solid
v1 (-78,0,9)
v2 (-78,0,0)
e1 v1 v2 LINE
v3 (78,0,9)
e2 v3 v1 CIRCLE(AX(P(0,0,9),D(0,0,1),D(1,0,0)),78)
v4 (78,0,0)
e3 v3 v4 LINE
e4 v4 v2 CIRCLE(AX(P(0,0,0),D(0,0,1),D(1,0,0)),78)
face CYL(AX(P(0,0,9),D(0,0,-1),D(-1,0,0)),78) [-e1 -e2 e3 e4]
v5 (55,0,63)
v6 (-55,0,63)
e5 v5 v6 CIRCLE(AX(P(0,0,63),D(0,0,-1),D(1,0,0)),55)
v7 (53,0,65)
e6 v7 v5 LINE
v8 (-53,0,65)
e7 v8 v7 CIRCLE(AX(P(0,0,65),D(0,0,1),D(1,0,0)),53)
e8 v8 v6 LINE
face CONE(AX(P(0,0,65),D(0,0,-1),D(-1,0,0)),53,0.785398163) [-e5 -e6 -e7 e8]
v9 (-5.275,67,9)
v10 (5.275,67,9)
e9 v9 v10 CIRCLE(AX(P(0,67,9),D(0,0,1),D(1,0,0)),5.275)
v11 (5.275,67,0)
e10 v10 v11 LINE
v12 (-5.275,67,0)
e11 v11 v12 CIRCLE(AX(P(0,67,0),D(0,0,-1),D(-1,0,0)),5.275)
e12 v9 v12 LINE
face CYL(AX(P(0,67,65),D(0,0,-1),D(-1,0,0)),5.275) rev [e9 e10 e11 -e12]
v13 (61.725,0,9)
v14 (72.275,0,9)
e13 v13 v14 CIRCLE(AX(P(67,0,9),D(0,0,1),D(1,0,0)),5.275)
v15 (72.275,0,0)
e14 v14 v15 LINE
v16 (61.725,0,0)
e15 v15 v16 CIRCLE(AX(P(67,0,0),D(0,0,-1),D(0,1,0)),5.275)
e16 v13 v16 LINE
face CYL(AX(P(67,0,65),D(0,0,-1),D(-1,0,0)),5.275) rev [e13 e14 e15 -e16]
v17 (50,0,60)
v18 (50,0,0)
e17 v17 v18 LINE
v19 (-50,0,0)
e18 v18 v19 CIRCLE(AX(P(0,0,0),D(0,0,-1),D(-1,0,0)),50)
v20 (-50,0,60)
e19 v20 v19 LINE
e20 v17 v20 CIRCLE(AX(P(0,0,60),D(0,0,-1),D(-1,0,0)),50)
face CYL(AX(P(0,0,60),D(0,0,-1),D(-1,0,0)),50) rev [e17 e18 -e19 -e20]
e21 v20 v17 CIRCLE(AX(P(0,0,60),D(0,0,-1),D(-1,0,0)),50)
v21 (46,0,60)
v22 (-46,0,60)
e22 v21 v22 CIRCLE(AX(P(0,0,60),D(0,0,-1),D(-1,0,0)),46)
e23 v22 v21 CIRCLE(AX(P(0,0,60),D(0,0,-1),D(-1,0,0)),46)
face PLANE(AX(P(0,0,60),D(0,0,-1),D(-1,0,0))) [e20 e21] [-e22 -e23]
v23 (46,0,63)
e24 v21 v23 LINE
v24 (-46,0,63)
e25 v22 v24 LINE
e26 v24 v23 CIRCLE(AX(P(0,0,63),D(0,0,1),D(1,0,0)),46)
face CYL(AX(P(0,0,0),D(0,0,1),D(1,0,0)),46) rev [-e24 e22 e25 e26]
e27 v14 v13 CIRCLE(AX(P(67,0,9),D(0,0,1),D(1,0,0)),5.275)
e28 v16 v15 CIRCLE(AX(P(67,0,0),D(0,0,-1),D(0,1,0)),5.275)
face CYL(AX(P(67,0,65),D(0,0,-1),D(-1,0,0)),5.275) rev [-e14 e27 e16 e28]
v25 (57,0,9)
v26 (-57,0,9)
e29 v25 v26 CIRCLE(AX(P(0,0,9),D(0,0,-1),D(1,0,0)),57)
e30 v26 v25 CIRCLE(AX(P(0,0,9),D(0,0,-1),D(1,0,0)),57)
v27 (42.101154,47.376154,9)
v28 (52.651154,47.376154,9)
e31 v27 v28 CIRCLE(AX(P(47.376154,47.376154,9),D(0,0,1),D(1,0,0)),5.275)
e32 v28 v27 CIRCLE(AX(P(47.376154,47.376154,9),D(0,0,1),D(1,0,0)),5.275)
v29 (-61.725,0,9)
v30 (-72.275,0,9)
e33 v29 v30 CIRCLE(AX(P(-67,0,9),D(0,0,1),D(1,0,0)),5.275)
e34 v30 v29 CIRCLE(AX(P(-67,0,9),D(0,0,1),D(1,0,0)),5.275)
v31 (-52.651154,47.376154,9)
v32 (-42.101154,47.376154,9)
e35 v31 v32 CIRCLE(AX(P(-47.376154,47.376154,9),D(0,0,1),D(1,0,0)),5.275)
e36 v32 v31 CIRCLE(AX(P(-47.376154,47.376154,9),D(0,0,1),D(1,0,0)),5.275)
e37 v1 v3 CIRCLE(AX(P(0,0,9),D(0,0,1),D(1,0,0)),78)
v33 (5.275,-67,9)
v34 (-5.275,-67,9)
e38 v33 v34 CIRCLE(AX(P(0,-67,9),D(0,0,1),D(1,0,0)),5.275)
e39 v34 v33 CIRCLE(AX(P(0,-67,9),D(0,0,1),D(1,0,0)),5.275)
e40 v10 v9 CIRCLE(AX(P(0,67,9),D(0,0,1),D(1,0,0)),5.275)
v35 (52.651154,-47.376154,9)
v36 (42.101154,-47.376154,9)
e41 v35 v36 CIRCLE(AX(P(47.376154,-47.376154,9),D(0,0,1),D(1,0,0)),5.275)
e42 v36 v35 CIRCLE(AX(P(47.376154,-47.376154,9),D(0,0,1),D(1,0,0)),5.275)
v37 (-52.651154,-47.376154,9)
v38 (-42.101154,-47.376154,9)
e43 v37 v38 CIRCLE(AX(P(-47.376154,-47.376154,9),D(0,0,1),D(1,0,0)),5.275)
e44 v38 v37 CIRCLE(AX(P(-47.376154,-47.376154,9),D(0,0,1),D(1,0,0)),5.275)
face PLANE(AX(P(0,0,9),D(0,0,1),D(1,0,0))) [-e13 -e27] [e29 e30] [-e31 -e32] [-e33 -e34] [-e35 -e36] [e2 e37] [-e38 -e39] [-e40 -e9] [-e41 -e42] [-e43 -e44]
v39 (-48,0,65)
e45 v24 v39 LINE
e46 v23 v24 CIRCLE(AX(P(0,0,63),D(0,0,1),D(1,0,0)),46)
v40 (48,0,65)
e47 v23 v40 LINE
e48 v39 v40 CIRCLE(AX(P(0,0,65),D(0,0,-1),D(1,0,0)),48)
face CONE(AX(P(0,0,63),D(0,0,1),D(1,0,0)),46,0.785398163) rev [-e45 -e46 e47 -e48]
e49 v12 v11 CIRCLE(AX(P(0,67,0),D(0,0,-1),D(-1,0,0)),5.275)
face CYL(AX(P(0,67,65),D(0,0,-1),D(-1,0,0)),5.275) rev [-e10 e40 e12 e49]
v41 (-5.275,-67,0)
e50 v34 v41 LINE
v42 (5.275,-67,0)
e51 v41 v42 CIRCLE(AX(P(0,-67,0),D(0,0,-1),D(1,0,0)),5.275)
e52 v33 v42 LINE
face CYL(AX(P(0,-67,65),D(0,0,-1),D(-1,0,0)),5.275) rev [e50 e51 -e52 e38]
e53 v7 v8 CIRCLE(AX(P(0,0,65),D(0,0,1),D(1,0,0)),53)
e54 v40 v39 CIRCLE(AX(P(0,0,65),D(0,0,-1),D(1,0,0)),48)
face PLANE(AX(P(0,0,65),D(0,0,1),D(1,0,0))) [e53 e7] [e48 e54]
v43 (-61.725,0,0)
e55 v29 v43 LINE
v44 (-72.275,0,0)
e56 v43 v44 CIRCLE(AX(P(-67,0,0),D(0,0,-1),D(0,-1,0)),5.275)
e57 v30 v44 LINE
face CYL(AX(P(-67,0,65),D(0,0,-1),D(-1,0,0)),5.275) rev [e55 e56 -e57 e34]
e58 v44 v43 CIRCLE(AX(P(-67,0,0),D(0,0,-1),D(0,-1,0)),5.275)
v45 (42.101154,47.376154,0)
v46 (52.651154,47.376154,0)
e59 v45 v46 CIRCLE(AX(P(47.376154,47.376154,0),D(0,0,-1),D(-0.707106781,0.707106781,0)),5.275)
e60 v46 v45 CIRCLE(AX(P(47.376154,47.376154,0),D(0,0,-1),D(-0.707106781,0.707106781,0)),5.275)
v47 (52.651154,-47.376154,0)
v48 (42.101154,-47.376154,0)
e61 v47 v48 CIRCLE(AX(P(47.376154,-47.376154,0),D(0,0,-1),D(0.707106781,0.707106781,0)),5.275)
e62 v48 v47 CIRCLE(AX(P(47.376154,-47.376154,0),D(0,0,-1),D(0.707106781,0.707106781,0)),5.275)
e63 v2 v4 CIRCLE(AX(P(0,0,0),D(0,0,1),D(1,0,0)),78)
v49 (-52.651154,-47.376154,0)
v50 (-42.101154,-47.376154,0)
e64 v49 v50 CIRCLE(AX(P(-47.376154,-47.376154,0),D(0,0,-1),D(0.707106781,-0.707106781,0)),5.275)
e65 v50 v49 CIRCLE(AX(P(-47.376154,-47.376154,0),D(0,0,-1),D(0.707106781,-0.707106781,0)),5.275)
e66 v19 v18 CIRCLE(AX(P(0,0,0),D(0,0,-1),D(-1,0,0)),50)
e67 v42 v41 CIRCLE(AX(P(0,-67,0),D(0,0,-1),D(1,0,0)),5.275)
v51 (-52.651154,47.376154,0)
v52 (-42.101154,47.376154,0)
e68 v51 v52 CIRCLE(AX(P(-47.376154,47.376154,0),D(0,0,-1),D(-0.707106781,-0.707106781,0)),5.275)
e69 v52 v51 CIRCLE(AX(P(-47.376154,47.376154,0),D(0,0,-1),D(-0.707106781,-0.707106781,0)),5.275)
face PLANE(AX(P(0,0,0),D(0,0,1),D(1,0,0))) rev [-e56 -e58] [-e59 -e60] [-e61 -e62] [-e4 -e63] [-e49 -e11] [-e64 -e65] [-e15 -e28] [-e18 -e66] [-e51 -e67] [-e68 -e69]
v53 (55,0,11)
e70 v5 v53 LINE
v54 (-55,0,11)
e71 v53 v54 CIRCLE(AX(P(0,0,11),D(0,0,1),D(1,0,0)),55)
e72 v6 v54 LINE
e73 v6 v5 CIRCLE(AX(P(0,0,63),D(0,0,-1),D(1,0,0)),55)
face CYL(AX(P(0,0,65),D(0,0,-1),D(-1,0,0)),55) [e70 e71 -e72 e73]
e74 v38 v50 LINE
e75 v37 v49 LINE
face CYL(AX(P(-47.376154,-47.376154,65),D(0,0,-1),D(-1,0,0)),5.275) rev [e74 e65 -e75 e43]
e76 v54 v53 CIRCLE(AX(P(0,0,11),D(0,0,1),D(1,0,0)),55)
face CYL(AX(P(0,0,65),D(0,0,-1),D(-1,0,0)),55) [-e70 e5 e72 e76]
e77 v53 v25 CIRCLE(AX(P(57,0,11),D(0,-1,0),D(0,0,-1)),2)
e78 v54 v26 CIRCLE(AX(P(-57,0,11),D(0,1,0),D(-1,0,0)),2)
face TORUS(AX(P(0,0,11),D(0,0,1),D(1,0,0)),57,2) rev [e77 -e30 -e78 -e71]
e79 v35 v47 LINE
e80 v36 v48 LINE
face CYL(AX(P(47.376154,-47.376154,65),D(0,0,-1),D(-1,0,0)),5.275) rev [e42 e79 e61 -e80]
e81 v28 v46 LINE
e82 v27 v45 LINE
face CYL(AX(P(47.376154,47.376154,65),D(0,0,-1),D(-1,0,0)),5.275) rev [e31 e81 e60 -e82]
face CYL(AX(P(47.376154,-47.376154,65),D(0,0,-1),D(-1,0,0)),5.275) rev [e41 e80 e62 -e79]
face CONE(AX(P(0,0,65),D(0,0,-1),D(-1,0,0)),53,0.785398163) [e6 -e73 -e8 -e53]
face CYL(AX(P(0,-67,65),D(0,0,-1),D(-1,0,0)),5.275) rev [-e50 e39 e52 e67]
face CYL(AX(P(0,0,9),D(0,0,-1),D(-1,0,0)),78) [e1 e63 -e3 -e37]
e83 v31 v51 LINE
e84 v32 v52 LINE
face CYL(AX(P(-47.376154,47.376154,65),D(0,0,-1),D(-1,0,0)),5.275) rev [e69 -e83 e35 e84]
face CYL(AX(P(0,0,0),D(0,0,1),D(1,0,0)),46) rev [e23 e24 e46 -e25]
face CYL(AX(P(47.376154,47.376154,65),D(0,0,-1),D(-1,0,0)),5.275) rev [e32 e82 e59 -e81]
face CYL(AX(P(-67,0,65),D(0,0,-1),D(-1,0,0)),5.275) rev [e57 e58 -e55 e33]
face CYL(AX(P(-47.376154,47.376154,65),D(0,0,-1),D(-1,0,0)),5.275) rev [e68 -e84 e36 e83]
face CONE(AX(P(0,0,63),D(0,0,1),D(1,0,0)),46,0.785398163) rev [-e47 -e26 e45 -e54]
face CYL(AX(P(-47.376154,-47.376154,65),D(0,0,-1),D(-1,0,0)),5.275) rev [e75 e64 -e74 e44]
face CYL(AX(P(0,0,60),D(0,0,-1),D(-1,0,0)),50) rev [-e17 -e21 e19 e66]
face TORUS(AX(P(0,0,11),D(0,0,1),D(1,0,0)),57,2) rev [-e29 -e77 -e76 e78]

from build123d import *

# Parameters (mm, degrees)
SKETCH1_R           = 78
BOSS_EXTRUDE1_DEPTH = 9
SKETCH2_R           = 55
BOSS_EXTRUDE2_DEPTH = 56
SKETCH3_R           = 50
CUT_EXTRUDE2_DEPTH  = 60
SKETCH4_R           = 46
CUT_EXTRUDE3_DEPTH  = 129.035151423
SKETCH5_R           = 5.275
CUT_EXTRUDE4_DEPTH  = 129.035151423
CIRPATTERN1_COUNT   = 8
CHAMFER1_SIZE       = 2
FILLET1_R           = 2


with BuildPart() as part:
    # Sketch1 → Boss-Extrude1 (new body)
    with BuildSketch(Plane.XY):
        Circle(SKETCH1_R)
    extrude(amount=BOSS_EXTRUDE1_DEPTH)

    # Sketch2 → Boss-Extrude2 (add)
    with BuildSketch(Plane.XY.offset(9)):
        Circle(SKETCH2_R)
    extrude(amount=BOSS_EXTRUDE2_DEPTH)

    # Sketch3 → Cut-Extrude2 (cut)
    with BuildSketch(Plane(origin=(0, 0, 0), x_dir=(-1, 0, 0), z_dir=(0, 0, -1))):
        Circle(SKETCH3_R)
    extrude(amount=-CUT_EXTRUDE2_DEPTH, mode=Mode.SUBTRACT)

    # Sketch4 → Cut-Extrude3 (cut, through all)
    with BuildSketch(Plane.XY.offset(65)):
        Circle(SKETCH4_R)
    extrude(amount=-CUT_EXTRUDE3_DEPTH, mode=Mode.SUBTRACT)

    # Sketch5 → Cut-Extrude4 (cut, through all)
    with BuildSketch(Plane(origin=(0, 0, 0), x_dir=(-1, 0, 0), z_dir=(0, 0, -1))):
        with Locations((0, 67)):
            Circle(SKETCH5_R)
    cut_extrude4 = extrude(amount=-CUT_EXTRUDE4_DEPTH, mode=Mode.SUBTRACT)

    # CirPattern1: Cut-Extrude4 ×8 about axis
    cirpattern1_axis = Axis((0, 0, 0), (0, 0, 1))
    for i in range(1, CIRPATTERN1_COUNT):
        add(cut_extrude4.rotate(cirpattern1_axis, i * 360 / CIRPATTERN1_COUNT), mode=Mode.SUBTRACT)

    # Chamfer1
    chamfer1_edges = [part.edges().sort_by_distance(p)[0] for p in [
        (-46, 0, 65),
        (-55, 0, 65),
    ]]
    chamfer(chamfer1_edges, length=CHAMFER1_SIZE)

    # Fillet1
    fillet1_edges = [part.edges().sort_by_distance(p)[0] for p in [
        (-55, 0, 9),
    ]]
    fillet(fillet1_edges, radius=FILLET1_R)


solid = part.part
